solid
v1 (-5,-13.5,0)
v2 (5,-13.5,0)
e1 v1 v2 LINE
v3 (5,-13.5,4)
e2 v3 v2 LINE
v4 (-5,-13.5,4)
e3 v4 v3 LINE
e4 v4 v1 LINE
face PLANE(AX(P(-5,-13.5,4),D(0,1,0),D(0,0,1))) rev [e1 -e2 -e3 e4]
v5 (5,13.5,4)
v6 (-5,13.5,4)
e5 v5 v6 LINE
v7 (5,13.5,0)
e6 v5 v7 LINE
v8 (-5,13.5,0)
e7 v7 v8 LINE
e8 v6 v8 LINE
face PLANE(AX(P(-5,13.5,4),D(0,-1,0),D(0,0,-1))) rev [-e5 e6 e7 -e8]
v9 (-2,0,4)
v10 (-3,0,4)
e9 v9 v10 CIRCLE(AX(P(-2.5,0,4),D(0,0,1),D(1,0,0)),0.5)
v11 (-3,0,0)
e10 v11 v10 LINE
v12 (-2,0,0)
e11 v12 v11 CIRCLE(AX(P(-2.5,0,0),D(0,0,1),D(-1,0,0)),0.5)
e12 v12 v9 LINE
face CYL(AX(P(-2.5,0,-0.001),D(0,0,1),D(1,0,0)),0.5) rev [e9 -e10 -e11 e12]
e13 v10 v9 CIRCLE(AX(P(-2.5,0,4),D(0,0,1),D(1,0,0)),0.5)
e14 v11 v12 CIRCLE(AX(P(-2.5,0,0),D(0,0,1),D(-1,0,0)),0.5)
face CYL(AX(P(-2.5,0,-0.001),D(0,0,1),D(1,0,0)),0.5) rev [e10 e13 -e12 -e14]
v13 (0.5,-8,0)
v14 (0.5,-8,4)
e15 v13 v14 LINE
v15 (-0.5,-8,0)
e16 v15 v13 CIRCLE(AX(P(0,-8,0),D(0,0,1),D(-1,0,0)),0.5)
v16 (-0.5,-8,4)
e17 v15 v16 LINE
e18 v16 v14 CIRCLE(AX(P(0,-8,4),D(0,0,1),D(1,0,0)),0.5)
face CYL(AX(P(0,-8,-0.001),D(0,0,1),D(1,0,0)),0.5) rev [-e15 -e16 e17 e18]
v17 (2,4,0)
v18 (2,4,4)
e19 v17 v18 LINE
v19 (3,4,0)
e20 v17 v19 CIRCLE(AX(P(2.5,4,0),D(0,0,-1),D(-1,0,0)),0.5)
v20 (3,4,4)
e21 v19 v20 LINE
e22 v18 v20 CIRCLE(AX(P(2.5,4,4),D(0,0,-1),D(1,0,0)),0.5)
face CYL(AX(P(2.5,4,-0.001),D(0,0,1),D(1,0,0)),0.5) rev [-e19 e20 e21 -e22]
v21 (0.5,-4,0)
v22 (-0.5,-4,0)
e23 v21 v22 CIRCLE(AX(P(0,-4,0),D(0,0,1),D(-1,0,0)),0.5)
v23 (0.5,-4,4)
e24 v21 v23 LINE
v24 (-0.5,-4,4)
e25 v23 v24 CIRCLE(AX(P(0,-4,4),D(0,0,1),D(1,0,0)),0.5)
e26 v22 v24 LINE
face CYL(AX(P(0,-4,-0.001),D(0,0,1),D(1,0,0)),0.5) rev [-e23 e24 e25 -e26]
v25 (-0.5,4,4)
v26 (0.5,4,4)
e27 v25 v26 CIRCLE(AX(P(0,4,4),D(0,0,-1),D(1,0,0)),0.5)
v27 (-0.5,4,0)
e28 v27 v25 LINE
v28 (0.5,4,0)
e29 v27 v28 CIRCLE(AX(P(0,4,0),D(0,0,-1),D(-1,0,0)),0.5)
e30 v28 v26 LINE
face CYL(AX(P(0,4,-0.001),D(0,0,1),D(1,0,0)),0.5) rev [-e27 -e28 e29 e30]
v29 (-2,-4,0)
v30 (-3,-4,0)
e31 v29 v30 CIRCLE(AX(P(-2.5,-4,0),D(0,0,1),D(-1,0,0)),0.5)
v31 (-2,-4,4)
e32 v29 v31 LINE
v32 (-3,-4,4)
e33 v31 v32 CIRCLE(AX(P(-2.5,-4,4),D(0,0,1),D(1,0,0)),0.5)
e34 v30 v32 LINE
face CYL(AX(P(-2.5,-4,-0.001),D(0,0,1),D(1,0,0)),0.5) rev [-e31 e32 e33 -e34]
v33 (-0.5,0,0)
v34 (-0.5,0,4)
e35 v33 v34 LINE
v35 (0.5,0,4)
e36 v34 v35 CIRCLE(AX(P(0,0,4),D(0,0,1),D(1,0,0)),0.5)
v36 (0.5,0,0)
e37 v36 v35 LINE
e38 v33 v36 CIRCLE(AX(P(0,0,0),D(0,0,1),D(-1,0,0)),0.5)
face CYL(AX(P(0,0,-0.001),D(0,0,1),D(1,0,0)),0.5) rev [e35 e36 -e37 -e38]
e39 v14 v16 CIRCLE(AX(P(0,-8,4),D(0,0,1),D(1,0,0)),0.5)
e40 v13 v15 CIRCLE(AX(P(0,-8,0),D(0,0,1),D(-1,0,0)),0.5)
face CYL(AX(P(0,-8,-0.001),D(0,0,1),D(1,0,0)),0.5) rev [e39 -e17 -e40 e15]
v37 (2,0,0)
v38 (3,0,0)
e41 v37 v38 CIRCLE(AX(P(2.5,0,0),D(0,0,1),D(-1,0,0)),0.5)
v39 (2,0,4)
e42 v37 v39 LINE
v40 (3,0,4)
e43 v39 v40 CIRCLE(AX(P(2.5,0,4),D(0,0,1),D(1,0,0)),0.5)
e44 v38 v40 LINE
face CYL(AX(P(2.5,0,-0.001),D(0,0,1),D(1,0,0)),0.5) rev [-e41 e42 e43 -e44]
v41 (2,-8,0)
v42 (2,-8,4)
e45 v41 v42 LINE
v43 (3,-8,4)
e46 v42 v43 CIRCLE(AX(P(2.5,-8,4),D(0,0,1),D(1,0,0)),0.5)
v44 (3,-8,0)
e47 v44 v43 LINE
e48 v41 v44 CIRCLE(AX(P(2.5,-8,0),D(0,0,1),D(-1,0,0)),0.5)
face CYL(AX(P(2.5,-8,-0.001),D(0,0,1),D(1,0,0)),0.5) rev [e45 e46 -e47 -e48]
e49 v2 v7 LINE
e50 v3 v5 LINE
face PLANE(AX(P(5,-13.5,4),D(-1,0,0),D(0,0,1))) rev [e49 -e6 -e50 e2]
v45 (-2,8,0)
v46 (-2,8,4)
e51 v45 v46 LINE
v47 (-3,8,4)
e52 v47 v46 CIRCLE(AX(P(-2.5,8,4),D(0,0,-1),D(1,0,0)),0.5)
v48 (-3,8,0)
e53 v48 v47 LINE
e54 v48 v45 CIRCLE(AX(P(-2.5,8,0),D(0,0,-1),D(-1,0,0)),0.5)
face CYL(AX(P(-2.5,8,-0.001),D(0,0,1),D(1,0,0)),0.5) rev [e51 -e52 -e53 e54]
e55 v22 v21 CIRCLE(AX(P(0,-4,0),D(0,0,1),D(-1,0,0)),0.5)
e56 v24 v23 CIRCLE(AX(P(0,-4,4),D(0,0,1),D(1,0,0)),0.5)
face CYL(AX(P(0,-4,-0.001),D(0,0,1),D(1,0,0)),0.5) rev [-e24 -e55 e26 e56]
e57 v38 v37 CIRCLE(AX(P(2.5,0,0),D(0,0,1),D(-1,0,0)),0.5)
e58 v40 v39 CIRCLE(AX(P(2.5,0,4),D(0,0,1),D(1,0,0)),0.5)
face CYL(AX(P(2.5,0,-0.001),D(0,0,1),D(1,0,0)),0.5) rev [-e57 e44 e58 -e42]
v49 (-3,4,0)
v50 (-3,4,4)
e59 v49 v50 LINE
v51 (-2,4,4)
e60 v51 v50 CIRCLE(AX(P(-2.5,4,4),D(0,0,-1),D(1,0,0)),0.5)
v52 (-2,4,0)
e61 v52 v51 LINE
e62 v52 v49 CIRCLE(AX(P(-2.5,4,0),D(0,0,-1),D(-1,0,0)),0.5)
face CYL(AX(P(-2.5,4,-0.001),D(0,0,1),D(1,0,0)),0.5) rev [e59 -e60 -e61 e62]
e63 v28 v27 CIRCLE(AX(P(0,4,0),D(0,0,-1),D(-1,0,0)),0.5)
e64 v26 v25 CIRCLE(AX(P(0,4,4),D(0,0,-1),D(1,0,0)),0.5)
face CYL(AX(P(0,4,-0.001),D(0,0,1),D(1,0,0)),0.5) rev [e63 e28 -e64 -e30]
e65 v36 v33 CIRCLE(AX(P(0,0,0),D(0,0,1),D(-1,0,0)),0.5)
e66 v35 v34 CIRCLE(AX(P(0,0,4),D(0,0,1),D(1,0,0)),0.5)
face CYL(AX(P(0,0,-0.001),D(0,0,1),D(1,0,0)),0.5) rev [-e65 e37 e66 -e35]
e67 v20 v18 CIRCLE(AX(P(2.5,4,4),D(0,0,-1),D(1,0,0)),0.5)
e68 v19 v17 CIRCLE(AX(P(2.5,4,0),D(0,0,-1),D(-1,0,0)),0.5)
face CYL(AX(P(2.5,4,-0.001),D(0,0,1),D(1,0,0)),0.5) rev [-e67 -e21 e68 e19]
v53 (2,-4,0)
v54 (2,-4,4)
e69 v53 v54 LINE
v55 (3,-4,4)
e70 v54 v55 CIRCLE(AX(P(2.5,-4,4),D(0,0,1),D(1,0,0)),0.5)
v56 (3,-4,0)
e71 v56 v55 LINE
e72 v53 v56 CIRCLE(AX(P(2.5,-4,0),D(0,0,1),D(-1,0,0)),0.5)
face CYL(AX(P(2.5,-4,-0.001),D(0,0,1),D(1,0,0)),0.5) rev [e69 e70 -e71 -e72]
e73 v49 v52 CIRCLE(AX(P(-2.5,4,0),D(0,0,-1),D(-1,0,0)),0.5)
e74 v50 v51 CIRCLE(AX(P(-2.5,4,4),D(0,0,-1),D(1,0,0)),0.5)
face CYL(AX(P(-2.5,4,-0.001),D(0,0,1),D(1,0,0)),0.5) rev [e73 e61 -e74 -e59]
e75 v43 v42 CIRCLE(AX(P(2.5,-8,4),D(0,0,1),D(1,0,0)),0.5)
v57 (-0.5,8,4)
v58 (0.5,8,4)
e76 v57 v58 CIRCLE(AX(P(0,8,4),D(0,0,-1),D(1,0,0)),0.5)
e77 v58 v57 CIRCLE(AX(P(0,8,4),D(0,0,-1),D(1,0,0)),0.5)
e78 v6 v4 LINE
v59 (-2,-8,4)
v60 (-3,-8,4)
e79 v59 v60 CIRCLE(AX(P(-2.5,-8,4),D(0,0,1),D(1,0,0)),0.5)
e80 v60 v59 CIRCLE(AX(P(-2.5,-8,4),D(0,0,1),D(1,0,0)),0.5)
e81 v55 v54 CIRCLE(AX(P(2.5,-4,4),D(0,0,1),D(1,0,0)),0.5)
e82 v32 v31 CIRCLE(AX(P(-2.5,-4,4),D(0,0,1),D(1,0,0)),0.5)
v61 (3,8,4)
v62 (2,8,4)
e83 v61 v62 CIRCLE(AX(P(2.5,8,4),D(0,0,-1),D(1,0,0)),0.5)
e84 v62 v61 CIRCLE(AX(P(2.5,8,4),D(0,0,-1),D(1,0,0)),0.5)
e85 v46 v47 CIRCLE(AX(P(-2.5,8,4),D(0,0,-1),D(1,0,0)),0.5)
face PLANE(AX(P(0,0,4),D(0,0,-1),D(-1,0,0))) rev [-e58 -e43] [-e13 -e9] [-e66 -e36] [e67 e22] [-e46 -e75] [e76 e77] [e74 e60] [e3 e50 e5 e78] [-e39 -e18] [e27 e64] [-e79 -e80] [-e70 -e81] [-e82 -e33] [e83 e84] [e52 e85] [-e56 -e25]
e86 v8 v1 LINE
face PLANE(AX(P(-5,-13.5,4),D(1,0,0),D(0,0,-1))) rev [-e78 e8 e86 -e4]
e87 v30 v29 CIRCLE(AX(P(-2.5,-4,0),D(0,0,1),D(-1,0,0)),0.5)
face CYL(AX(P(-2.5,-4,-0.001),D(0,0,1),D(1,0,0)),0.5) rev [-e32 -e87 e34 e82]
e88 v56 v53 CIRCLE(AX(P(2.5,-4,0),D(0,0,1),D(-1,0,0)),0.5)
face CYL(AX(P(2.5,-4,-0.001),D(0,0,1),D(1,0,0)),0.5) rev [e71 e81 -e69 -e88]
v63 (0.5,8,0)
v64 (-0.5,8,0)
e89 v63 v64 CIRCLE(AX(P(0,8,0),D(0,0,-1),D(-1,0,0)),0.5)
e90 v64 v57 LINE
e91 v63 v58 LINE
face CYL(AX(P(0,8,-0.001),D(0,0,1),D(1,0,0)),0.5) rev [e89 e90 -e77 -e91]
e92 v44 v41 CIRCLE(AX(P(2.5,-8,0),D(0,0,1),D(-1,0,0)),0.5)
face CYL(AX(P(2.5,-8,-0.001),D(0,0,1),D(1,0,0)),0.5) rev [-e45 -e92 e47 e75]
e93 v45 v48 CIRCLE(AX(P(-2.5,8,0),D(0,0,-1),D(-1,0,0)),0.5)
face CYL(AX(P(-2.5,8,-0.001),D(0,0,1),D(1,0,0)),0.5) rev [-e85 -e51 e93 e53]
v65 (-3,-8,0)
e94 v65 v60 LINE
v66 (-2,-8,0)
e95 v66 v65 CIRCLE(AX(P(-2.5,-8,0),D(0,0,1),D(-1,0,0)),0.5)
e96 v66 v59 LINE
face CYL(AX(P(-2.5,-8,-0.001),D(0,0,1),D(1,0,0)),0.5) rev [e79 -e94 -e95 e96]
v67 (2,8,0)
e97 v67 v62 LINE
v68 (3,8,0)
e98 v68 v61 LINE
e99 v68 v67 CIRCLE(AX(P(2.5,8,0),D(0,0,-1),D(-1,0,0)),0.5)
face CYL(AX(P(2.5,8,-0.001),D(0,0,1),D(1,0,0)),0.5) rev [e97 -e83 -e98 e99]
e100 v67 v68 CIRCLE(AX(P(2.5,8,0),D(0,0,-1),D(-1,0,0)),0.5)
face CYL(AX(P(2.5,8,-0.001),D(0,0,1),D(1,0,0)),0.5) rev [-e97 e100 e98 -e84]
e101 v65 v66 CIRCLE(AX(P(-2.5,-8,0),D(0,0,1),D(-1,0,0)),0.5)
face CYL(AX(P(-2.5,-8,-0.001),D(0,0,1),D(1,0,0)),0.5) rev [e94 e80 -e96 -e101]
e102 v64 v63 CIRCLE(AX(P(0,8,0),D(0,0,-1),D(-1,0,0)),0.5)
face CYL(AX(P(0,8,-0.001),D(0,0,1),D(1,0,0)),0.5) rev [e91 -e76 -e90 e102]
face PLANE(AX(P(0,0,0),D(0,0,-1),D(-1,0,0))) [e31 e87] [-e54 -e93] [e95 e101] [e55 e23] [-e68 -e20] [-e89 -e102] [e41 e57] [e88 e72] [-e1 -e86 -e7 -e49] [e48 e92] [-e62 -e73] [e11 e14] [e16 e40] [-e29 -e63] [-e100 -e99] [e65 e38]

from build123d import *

# Parameters (mm, degrees)
SKETCH_1_W               = 10
SKETCH_1_H               = 27
EXTRUDE_1_DEPTH          = 4
CUT_EXTRUDE_1_REACH      = 16.942
SKETCH_2_R               = 0.5
PATTERN_LINEAR_2_COUNT   = 3
PATTERN_LINEAR_2_PITCH   = 4
MIRROR_1_COPY_1_REACH    = 16.942
MIRROR_1_COPY_1_SKETCH_R = 0.5
MIRROR_1_COPY_2_REACH    = 16.942
MIRROR_1_COPY_2_SKETCH_R = 0.5


with BuildPart() as part:
    # 草图1 → 凸台-拉伸1 (new body)
    with BuildSketch(Plane.XY):
        Rectangle(SKETCH_1_W, SKETCH_1_H)
    extrude(amount=EXTRUDE_1_DEPTH)

    # 草图2 → 切除-拉伸1 (cut, up to next)
    with BuildSketch(Plane.XY.offset(4), mode=Mode.PRIVATE) as cut_extrude_1_sk1:
        Circle(SKETCH_2_R)
    cut_extrude_1_tool1 = extrude(cut_extrude_1_sk1.sketch, amount=-CUT_EXTRUDE_1_REACH, mode=Mode.PRIVATE) & part.part
    # 草图2 → 切除-拉伸1 (cut, up to next)
    with BuildSketch(Plane.XY.offset(4), mode=Mode.PRIVATE) as cut_extrude_1_sk2:
        with Locations((-2.5, 0)):
            Circle(SKETCH_2_R)
    cut_extrude_1_tool2 = extrude(cut_extrude_1_sk2.sketch, amount=-CUT_EXTRUDE_1_REACH, mode=Mode.PRIVATE) & part.part
    # 草图2 → 切除-拉伸1 (cut, up to next)
    with BuildSketch(Plane.XY.offset(4), mode=Mode.PRIVATE) as cut_extrude_1_sk3:
        with Locations((2.5, 0)):
            Circle(SKETCH_2_R)
    cut_extrude_1_tool3 = extrude(cut_extrude_1_sk3.sketch, amount=-CUT_EXTRUDE_1_REACH, mode=Mode.PRIVATE) & part.part
    cut_extrude_1_1 = cut_extrude_1_tool1.solids().sort_by_distance((0, 0, 4))[0]
    add(cut_extrude_1_1, mode=Mode.SUBTRACT)
    cut_extrude_1_2 = cut_extrude_1_tool2.solids().sort_by_distance((-2.5, 0, 4))[0]
    add(cut_extrude_1_2, mode=Mode.SUBTRACT)
    cut_extrude_1_3 = cut_extrude_1_tool3.solids().sort_by_distance((2.5, 0, 4))[0]
    add(cut_extrude_1_3, mode=Mode.SUBTRACT)
    cut_extrude_1 = cut_extrude_1_1 + cut_extrude_1_2 + cut_extrude_1_3  # 切除-拉伸1 as one shape, for the pattern or mirror that repeats it

    # 阵列(线性)2: 切除-拉伸1 ×3
    with Locations(*[(0, -i * PATTERN_LINEAR_2_PITCH, 0) for i in range(1, PATTERN_LINEAR_2_COUNT)]):
        add(cut_extrude_1, mode=Mode.SUBTRACT)

    # 镜向1 copy 1 sketch → 镜向1 copy 1 (cut, up to next)
    with BuildSketch(Plane(origin=(0, 4, 4), x_dir=(1, 0, 0), z_dir=(0, 0, 1)), mode=Mode.PRIVATE) as mirror_1_copy_1_sk1:
        Circle(MIRROR_1_COPY_1_SKETCH_R)
    mirror_1_copy_1_tool1 = extrude(mirror_1_copy_1_sk1.sketch, amount=-MIRROR_1_COPY_1_REACH, mode=Mode.PRIVATE) & part.part
    # 镜向1 copy 1 sketch → 镜向1 copy 1 (cut, up to next)
    with BuildSketch(Plane(origin=(0, 4, 4), x_dir=(1, 0, 0), z_dir=(0, 0, 1)), mode=Mode.PRIVATE) as mirror_1_copy_1_sk2:
        with Locations((-2.5, 0)):
            Circle(MIRROR_1_COPY_1_SKETCH_R)
    mirror_1_copy_1_tool2 = extrude(mirror_1_copy_1_sk2.sketch, amount=-MIRROR_1_COPY_1_REACH, mode=Mode.PRIVATE) & part.part
    # 镜向1 copy 1 sketch → 镜向1 copy 1 (cut, up to next)
    with BuildSketch(Plane(origin=(0, 4, 4), x_dir=(1, 0, 0), z_dir=(0, 0, 1)), mode=Mode.PRIVATE) as mirror_1_copy_1_sk3:
        with Locations((2.5, 0)):
            Circle(MIRROR_1_COPY_1_SKETCH_R)
    mirror_1_copy_1_tool3 = extrude(mirror_1_copy_1_sk3.sketch, amount=-MIRROR_1_COPY_1_REACH, mode=Mode.PRIVATE) & part.part
    add(mirror_1_copy_1_tool1.solids().sort_by_distance((0, 4, 4))[0], mode=Mode.SUBTRACT)
    add(mirror_1_copy_1_tool2.solids().sort_by_distance((-2.5, 4, 4))[0], mode=Mode.SUBTRACT)
    add(mirror_1_copy_1_tool3.solids().sort_by_distance((2.5, 4, 4))[0], mode=Mode.SUBTRACT)

    # 镜向1 copy 2 sketch → 镜向1 copy 2 (cut, up to next)
    with BuildSketch(Plane(origin=(0, 8, 4), x_dir=(1, 0, 0), z_dir=(0, 0, 1)), mode=Mode.PRIVATE) as mirror_1_copy_2_sk1:
        Circle(MIRROR_1_COPY_2_SKETCH_R)
    mirror_1_copy_2_tool1 = extrude(mirror_1_copy_2_sk1.sketch, amount=-MIRROR_1_COPY_2_REACH, mode=Mode.PRIVATE) & part.part
    # 镜向1 copy 2 sketch → 镜向1 copy 2 (cut, up to next)
    with BuildSketch(Plane(origin=(0, 8, 4), x_dir=(1, 0, 0), z_dir=(0, 0, 1)), mode=Mode.PRIVATE) as mirror_1_copy_2_sk2:
        with Locations((-2.5, 0)):
            Circle(MIRROR_1_COPY_2_SKETCH_R)
    mirror_1_copy_2_tool2 = extrude(mirror_1_copy_2_sk2.sketch, amount=-MIRROR_1_COPY_2_REACH, mode=Mode.PRIVATE) & part.part
    # 镜向1 copy 2 sketch → 镜向1 copy 2 (cut, up to next)
    with BuildSketch(Plane(origin=(0, 8, 4), x_dir=(1, 0, 0), z_dir=(0, 0, 1)), mode=Mode.PRIVATE) as mirror_1_copy_2_sk3:
        with Locations((2.5, 0)):
            Circle(MIRROR_1_COPY_2_SKETCH_R)
    mirror_1_copy_2_tool3 = extrude(mirror_1_copy_2_sk3.sketch, amount=-MIRROR_1_COPY_2_REACH, mode=Mode.PRIVATE) & part.part
    add(mirror_1_copy_2_tool1.solids().sort_by_distance((0, 8, 4))[0], mode=Mode.SUBTRACT)
    add(mirror_1_copy_2_tool2.solids().sort_by_distance((-2.5, 8, 4))[0], mode=Mode.SUBTRACT)
    add(mirror_1_copy_2_tool3.solids().sort_by_distance((2.5, 8, 4))[0], mode=Mode.SUBTRACT)


solid = part.part
